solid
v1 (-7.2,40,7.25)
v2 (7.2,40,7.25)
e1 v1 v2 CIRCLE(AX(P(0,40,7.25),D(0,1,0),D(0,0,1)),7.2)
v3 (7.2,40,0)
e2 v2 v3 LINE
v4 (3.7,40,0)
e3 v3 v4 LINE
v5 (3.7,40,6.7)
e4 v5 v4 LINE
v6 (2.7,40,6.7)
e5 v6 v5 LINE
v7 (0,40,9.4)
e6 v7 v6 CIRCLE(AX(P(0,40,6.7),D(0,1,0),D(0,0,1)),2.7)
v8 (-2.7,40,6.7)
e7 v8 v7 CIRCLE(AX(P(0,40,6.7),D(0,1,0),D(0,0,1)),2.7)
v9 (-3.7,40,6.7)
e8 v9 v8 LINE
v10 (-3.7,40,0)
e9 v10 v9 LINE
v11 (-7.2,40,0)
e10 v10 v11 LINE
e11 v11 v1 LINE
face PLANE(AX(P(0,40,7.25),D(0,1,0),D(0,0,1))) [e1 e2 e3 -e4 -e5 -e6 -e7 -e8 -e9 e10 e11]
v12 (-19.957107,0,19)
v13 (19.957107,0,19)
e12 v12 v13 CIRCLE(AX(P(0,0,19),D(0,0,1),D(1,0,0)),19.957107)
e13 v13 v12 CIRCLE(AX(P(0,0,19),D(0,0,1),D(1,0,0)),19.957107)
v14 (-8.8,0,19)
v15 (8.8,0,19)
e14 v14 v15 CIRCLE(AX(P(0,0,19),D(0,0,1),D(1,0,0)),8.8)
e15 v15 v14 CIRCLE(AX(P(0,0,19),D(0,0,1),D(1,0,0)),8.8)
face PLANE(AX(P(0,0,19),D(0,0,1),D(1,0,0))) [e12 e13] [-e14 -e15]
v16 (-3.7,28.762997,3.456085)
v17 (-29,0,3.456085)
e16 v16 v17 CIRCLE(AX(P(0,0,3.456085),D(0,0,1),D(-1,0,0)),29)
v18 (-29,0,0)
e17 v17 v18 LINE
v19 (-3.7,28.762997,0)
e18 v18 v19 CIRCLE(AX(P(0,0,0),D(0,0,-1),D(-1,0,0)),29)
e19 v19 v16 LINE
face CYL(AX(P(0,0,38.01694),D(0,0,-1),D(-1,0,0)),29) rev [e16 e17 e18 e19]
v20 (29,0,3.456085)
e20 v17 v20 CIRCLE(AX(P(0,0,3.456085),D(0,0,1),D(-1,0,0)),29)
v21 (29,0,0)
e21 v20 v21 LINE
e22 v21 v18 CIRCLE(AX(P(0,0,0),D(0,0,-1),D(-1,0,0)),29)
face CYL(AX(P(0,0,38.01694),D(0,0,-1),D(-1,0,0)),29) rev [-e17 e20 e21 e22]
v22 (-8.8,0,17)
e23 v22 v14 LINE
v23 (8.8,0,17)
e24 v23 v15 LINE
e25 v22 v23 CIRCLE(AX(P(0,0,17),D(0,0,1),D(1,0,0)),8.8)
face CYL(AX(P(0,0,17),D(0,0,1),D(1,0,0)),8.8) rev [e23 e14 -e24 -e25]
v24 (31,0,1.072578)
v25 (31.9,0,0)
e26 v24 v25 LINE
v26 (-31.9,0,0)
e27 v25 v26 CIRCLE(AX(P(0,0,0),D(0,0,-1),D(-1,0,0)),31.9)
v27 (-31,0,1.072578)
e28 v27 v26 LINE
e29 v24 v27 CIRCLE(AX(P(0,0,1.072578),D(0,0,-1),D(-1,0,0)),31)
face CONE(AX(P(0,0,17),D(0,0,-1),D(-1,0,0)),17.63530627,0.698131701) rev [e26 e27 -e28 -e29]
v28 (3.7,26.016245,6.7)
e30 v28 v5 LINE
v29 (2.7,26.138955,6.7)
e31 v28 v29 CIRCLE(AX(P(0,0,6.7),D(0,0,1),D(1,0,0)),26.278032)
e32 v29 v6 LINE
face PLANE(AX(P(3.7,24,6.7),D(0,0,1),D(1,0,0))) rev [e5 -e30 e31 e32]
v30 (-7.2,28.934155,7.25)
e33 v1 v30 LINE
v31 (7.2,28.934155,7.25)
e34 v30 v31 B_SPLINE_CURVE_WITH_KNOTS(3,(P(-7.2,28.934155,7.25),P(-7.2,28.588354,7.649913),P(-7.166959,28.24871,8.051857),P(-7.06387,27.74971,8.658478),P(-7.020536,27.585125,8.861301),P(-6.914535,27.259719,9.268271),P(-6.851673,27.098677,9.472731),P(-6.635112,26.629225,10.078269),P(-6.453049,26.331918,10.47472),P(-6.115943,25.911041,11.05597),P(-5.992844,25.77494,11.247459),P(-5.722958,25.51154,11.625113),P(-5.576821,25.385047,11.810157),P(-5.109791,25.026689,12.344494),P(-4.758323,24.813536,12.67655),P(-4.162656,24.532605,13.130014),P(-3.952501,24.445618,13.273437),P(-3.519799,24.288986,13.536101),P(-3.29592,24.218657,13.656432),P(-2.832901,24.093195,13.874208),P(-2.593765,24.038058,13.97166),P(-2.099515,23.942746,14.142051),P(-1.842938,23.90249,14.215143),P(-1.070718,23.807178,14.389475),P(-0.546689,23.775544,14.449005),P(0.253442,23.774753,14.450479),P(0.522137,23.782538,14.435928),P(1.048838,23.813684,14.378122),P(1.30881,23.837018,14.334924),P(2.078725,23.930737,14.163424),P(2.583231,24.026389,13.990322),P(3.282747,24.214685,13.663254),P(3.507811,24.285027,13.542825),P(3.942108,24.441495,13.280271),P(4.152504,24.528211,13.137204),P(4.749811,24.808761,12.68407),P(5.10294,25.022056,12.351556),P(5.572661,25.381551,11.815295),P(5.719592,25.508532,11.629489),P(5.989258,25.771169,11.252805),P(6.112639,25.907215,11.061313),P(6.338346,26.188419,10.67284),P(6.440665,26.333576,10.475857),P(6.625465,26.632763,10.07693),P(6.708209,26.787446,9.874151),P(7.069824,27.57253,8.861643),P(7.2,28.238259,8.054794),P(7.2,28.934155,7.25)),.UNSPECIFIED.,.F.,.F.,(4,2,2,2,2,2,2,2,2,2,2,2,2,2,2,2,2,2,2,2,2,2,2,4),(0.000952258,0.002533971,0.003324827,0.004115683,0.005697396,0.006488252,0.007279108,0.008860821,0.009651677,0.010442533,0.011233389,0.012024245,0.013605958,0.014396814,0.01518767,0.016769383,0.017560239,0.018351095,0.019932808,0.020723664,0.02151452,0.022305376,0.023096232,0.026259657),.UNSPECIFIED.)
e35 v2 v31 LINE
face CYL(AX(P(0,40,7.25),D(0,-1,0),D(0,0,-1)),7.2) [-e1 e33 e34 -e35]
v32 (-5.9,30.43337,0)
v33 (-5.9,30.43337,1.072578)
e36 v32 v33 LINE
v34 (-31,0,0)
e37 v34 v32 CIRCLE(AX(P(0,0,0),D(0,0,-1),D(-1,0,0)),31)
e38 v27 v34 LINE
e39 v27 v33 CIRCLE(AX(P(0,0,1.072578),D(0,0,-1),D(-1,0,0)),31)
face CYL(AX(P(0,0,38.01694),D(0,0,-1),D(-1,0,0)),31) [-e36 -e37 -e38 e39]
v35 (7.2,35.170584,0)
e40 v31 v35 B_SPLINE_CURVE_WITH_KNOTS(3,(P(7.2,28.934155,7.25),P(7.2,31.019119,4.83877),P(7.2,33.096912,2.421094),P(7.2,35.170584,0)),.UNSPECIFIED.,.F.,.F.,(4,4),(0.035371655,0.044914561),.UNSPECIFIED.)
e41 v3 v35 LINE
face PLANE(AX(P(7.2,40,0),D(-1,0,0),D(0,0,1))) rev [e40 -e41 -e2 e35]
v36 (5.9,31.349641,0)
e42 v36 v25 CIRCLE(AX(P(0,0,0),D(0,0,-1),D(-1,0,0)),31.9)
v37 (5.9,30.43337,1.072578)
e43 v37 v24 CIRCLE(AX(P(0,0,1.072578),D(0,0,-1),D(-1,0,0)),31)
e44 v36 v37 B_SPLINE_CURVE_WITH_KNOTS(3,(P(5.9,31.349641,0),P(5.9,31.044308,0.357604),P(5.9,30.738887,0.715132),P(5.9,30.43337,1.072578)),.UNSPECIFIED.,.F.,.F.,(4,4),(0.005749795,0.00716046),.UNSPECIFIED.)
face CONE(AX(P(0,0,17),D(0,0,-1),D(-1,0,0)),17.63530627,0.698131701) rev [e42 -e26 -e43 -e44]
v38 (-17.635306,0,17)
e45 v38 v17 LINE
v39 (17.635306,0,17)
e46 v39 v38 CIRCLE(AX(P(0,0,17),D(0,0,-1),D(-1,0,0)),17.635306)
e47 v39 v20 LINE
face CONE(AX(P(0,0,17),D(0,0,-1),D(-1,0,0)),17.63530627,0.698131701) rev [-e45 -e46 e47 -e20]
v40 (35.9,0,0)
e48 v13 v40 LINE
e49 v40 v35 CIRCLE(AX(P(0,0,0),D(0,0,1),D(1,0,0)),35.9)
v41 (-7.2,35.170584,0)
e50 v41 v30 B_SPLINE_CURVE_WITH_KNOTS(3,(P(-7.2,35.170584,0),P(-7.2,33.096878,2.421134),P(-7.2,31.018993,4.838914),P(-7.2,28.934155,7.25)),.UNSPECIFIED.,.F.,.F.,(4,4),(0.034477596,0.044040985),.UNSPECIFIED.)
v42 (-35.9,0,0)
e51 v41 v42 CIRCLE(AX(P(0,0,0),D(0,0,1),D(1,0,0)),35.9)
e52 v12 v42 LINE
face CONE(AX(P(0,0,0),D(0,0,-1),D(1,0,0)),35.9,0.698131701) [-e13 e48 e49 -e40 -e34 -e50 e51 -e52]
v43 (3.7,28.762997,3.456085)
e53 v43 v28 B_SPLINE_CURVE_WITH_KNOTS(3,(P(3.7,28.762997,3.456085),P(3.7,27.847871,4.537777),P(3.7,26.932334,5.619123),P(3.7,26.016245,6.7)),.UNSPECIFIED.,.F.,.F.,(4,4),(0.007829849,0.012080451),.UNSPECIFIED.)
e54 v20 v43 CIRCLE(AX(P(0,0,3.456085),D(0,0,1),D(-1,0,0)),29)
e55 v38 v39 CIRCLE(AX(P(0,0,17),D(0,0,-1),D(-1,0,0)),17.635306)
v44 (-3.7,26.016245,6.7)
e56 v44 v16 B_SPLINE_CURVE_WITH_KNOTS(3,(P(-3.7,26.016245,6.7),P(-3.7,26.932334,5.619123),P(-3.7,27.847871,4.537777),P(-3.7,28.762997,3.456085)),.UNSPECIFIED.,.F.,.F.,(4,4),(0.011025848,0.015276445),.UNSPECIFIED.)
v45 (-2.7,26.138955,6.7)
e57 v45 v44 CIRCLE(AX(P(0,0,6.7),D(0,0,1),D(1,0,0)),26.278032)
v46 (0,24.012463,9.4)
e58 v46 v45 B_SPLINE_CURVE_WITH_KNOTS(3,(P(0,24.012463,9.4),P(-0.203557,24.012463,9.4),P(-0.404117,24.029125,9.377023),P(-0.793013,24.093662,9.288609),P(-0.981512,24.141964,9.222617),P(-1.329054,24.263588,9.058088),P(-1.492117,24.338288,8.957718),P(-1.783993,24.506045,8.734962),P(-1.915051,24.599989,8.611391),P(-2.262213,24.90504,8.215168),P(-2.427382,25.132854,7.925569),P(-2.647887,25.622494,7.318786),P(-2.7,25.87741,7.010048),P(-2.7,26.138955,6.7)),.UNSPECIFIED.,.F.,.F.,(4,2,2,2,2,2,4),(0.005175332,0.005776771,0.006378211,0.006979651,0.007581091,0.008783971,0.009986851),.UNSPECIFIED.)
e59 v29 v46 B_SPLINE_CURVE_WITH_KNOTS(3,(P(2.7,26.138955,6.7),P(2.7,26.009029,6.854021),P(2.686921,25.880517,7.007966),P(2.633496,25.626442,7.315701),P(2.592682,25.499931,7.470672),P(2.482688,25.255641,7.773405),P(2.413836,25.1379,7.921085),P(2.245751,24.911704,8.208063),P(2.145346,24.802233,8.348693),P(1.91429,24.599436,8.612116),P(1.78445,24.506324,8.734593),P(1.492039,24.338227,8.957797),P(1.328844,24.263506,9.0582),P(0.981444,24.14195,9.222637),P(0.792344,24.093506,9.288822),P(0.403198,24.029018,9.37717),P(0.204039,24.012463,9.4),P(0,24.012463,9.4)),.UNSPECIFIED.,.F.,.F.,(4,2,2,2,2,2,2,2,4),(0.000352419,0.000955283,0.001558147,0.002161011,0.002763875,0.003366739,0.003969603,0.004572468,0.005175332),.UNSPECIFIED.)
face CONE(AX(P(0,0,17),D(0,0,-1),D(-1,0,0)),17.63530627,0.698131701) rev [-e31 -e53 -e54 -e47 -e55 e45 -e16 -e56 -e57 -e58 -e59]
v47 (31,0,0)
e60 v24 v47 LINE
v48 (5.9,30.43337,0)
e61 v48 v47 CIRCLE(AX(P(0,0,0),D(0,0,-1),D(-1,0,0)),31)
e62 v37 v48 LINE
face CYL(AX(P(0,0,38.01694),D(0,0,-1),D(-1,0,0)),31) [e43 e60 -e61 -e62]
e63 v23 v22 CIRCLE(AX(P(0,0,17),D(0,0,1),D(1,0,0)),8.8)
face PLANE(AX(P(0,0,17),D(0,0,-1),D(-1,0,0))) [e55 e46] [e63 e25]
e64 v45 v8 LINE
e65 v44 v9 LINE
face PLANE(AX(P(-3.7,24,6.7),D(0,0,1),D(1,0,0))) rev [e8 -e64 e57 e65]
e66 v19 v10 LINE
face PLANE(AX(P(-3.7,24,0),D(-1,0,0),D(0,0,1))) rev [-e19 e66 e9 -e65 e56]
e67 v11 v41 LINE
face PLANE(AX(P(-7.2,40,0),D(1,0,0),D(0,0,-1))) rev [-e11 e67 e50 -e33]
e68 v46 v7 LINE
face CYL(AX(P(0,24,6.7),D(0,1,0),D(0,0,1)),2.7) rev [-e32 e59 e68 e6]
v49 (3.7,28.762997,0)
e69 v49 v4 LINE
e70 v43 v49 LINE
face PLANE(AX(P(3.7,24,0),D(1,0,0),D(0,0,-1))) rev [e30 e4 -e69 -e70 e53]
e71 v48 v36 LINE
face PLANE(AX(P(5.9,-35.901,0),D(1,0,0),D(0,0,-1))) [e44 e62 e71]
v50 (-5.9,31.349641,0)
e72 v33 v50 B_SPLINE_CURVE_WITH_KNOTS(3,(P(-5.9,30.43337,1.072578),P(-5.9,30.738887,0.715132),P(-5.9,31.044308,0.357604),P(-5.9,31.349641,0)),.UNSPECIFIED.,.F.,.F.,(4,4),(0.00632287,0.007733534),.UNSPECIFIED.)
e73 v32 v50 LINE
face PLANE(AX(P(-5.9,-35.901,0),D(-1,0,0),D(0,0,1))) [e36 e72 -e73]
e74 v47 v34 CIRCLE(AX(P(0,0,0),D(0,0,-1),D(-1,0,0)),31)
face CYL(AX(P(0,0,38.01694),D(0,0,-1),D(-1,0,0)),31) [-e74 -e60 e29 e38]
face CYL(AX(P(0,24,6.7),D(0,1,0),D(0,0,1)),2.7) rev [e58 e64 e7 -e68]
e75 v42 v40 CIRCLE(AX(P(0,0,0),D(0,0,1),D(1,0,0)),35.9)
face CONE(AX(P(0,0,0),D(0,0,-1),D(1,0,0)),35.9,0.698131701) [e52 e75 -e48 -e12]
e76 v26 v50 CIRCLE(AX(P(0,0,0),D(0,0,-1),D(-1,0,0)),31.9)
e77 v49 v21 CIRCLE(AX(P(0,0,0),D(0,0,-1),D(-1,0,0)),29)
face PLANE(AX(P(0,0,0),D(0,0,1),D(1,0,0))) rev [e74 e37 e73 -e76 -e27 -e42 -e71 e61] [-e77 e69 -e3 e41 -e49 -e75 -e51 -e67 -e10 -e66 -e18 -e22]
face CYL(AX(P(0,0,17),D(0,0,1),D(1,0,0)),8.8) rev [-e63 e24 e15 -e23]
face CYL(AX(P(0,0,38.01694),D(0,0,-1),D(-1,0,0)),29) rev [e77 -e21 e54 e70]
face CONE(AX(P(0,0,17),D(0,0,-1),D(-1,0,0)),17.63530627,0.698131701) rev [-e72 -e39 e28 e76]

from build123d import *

# Parameters (mm, degrees)
SKETCH_1_R           = 35.9
EXTRUDE_1_DEPTH      = 19
EXTRUDE_1_TAPER      = 40
EXTRUDE_2_DEPTH      = 40
EXTRUDE_3_REACH      = 59.007
SKETCH_8_R           = 31
SKETCH_8_R_2         = 29
SKETCH_9_R           = 8.8
CUT_EXTRUDE_1_DEPTH  = 2
CUT_EXTRUDE_2_DEPTH  = 16
EXTRUDE_4_REACH      = 88.085
EXTRUDE_4_END_RADIUS = 31
SKETCH_11_W          = 2.2
SKETCH_11_H          = 6.7


with BuildPart() as part:
    # 草图1 → 凸台-拉伸1 (new body)
    with BuildSketch(Plane.XY):
        Circle(SKETCH_1_R)
    extrude(amount=EXTRUDE_1_DEPTH, taper=EXTRUDE_1_TAPER)

    # 草图6 → 凸台-拉伸2 (add)
    with BuildSketch(Plane(origin=(0, 0, 0), x_dir=(1, 0, 0), z_dir=(0, 1, 0))):
        with BuildLine():
            Line((-7.2, 0), (-7.2, -7.25))
            ThreePointArc((-7.2, -7.25), (0, -14.45), (7.2, -7.25))
            Line((7.2, -7.25), (7.2, 0))
            Line((7.2, 0), (-7.2, 0))
        make_face()
    extrude(amount=EXTRUDE_2_DEPTH)

    # 草图7 → 切除-旋转1 (revolve, cut)
    with BuildSketch(Plane(origin=(0, 0, 0), x_dir=(0, 0, -1), z_dir=(1, 0, 0)), mode=Mode.PRIVATE) as cut_revolve_1_sk:
        Polygon((-17, 0), (-17, -17.63530627), (0, -31.9), (0, 0), align=None)
    revolve(cut_revolve_1_sk.sketch.rotate(Axis((0, 0, -9.48864884), (0, 0, 1)), 270), axis=Axis((0, 0, -9.48864884), (0, 0, 1)), mode=Mode.SUBTRACT)

    # 凸台-拉伸3: up to this cone (the profile starts inside it)
    extrude_3_end = Plane(origin=(0, 0, 0), z_dir=(0, 0, -1)).offset(-38.016938604) * Cone(1e-06, 108.599579987, 129.423938604, align=(Align.CENTER, Align.CENTER, Align.MIN), mode=Mode.PRIVATE)
    # 草图8 → 凸台-拉伸3 (add, up to the surface)
    with BuildSketch(Plane(origin=(0, 0, 0), x_dir=(-1, 0, 0), z_dir=(0, 0, -1)), mode=Mode.PRIVATE) as extrude_3_sk1:
        Circle(SKETCH_8_R)
        Circle(SKETCH_8_R_2, mode=Mode.SUBTRACT)
    extrude_3_tool1 = extrude(extrude_3_sk1.sketch, amount=-EXTRUDE_3_REACH, mode=Mode.PRIVATE) & extrude_3_end
    add(extrude_3_tool1.solids().sort_by_distance((30.123188, 0, 0))[0])

    # 草图9 → 切除-拉伸1 (cut)
    with BuildSketch(Plane.XY.offset(19)):
        Circle(SKETCH_9_R)
    extrude(amount=-CUT_EXTRUDE_1_DEPTH, mode=Mode.SUBTRACT)

    # 草图10 → 切除-拉伸2 (cut)
    with BuildSketch(Plane(origin=(0, 40, 0), x_dir=(1, 0, 0), z_dir=(0, 1, 0))):
        with BuildLine():
            Line((3.7, 0), (3.7, -6.7))
            Line((3.7, -6.7), (2.7, -6.7))
            ThreePointArc((2.7, -6.7), (0, -9.4), (-2.7, -6.7))
            Line((-2.7, -6.7), (-3.7, -6.7))
            Line((-3.7, -6.7), (-3.7, 0))
            Line((-3.7, 0), (3.7, 0))
        make_face()
    extrude(amount=-CUT_EXTRUDE_2_DEPTH, mode=Mode.SUBTRACT)

    # 凸台-拉伸4: up to this cylinder (the profile starts outside it)
    extrude_4_end = Plane(origin=(0, 0, 3.35), z_dir=(0, 0, -1)) * Cylinder(EXTRUDE_4_END_RADIUS, 239.17, mode=Mode.PRIVATE)
    # 草图11 → 凸台-拉伸4 (add, up to the surface)
    with BuildSketch(Plane(origin=(0, 40, 0), x_dir=(1, 0, 0), z_dir=(0, 1, 0)), mode=Mode.PRIVATE) as extrude_4_sk1:
        with Locations((-4.8, -3.35)):
            Rectangle(SKETCH_11_W, SKETCH_11_H)
    extrude_4_tool1 = extrude(extrude_4_sk1.sketch, amount=-EXTRUDE_4_REACH, mode=Mode.PRIVATE) - extrude_4_end
    add(extrude_4_tool1.solids().sort_by_distance((-4.8, 40, 3.35))[0])
    # 草图11 → 凸台-拉伸4 (add, up to the surface)
    with BuildSketch(Plane(origin=(0, 40, 0), x_dir=(1, 0, 0), z_dir=(0, 1, 0)), mode=Mode.PRIVATE) as extrude_4_sk2:
        with Locations((4.8, -3.35)):
            Rectangle(SKETCH_11_W, SKETCH_11_H)
    extrude_4_tool2 = extrude(extrude_4_sk2.sketch, amount=-EXTRUDE_4_REACH, mode=Mode.PRIVATE) - extrude_4_end
    add(extrude_4_tool2.solids().sort_by_distance((4.8, 40, 3.35))[0])


solid = part.part
